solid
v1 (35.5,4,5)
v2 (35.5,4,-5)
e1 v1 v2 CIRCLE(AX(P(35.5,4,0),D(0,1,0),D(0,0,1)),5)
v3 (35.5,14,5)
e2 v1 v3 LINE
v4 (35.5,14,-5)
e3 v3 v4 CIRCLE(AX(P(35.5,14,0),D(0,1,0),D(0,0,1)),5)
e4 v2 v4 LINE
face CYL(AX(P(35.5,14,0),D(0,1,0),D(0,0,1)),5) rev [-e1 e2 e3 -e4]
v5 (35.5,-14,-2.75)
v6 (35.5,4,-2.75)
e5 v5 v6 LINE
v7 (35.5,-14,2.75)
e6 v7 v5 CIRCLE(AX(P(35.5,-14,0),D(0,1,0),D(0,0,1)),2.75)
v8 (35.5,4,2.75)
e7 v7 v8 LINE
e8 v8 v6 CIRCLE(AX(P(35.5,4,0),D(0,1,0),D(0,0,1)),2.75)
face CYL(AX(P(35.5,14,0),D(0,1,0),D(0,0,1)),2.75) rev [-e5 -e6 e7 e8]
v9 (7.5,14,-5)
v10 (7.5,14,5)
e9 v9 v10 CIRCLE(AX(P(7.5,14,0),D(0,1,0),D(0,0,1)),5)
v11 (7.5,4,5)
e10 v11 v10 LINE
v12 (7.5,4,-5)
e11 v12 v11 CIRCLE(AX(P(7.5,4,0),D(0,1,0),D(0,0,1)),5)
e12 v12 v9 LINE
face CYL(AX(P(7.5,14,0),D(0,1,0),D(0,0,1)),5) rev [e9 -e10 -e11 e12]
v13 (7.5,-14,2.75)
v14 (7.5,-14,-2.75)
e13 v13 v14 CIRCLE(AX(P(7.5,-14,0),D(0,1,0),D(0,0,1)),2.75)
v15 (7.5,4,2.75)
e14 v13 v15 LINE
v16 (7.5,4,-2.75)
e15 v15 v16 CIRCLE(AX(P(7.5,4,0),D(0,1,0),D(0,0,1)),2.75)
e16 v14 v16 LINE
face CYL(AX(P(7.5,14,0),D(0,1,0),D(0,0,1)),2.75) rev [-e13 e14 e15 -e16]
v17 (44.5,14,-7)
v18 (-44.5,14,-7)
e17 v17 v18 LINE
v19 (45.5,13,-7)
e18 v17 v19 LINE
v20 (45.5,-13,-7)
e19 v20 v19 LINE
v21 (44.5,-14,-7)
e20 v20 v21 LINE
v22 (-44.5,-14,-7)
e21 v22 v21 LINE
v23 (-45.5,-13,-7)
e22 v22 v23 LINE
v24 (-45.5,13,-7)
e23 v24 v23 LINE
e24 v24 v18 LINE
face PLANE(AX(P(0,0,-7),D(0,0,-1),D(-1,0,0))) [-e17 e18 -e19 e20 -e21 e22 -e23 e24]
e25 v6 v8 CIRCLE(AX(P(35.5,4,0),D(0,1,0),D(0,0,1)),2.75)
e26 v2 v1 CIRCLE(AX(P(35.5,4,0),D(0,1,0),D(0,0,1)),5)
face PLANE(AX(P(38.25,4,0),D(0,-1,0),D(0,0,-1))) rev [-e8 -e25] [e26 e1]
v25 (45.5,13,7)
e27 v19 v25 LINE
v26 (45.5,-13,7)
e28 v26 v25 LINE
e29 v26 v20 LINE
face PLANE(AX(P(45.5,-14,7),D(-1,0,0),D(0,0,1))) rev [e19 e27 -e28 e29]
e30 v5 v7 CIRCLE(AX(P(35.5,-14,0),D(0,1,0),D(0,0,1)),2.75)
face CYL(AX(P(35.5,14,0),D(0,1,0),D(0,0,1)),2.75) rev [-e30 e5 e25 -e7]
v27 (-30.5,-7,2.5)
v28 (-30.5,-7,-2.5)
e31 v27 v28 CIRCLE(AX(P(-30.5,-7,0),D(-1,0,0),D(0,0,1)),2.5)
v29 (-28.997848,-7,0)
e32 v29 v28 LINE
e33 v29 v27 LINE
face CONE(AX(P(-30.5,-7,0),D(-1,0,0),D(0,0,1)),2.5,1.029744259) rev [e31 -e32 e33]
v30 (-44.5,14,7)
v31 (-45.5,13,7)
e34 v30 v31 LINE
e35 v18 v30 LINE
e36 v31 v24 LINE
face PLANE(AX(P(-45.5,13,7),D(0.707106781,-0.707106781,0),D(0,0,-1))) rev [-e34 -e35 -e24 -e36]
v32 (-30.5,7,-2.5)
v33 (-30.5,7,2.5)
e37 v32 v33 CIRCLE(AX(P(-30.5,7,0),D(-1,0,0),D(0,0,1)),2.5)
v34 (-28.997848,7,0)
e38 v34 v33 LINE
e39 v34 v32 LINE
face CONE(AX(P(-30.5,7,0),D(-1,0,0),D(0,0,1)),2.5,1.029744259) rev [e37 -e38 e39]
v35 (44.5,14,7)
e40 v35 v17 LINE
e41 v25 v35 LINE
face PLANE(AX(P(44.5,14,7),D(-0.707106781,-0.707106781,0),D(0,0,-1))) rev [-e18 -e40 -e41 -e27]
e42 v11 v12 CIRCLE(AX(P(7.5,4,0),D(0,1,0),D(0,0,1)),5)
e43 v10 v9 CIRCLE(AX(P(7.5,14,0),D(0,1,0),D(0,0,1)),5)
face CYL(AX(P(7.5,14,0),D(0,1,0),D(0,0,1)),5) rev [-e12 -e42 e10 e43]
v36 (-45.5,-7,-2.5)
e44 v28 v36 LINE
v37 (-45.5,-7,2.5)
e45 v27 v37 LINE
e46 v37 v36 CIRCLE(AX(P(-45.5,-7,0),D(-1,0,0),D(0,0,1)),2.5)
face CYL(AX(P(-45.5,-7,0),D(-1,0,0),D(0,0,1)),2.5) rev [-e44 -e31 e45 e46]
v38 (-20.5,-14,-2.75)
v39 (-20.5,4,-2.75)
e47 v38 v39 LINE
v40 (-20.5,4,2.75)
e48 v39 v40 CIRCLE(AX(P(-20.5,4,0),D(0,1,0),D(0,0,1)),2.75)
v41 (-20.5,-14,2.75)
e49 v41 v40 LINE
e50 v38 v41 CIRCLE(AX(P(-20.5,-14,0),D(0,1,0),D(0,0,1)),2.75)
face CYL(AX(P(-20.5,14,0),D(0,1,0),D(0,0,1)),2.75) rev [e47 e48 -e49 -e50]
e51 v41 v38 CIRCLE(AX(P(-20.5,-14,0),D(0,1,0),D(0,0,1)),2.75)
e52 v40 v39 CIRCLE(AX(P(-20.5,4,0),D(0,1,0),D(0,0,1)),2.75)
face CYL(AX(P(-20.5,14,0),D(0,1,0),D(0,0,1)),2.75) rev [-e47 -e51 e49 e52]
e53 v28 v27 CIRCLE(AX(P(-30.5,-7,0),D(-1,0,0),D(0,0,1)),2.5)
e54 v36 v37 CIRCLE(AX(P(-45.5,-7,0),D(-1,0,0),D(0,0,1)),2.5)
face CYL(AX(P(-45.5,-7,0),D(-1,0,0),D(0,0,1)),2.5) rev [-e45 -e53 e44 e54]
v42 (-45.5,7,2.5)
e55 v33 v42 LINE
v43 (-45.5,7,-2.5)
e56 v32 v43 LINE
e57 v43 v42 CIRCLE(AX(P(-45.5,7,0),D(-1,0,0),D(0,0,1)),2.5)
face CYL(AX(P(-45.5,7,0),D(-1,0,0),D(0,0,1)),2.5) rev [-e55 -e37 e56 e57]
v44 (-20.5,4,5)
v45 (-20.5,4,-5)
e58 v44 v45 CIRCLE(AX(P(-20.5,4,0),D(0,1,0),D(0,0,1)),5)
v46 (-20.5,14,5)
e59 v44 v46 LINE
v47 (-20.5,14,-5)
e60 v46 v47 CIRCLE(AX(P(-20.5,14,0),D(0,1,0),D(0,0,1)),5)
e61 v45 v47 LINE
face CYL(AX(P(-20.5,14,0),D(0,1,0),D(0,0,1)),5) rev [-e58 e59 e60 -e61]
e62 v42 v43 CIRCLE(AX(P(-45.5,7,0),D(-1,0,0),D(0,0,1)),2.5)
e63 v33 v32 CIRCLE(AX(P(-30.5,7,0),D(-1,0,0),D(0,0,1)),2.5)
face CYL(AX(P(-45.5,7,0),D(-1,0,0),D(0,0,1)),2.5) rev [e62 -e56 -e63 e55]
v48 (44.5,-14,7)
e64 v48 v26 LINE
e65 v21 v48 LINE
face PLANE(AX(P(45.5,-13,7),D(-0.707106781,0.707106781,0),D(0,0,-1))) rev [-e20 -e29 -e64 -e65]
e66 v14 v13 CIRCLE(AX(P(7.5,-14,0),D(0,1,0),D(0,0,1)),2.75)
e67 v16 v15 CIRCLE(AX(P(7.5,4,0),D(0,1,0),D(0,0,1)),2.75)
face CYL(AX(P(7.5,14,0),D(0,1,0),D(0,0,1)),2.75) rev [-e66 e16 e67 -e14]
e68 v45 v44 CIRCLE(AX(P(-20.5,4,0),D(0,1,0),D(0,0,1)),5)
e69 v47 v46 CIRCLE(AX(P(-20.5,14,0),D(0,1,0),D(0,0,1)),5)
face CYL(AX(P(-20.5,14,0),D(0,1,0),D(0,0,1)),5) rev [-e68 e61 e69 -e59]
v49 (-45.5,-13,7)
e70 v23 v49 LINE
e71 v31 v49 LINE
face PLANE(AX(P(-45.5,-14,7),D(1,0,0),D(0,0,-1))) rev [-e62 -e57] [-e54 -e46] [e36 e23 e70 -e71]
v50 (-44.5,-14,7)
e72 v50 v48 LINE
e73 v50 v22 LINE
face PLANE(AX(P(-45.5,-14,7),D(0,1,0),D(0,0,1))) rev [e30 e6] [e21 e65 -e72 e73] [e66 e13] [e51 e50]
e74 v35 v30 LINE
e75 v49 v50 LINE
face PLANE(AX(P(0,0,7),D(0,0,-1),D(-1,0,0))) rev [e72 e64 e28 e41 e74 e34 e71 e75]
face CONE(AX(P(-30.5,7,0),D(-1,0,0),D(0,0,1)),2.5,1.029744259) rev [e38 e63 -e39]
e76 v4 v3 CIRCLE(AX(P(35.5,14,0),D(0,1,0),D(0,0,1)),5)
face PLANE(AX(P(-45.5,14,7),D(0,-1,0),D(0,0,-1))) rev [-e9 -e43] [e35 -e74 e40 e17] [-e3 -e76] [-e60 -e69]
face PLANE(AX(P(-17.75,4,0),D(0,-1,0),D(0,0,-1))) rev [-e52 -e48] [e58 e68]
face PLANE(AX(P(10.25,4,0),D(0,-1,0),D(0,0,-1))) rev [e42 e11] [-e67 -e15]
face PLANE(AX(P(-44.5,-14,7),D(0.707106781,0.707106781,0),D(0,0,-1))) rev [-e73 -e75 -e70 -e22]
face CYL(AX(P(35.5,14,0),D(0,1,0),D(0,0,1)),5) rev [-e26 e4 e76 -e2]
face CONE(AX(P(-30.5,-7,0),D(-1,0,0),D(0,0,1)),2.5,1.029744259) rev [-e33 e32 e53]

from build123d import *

# Parameters (mm, degrees)
SKETCH1_W                                            = 91
SKETCH1_H                                            = 28
BOSS_EXTRUDE1_DEPTH                                  = 7
M6_TAPPED_HOLE1_D                                    = 5
M6_TAPPED_HOLE1_DEPTH                                = 15
M6_TAPPED_HOLE1_TIP                                  = 1.502151548
HOLE_SIZE_PER_SOCKET_HEAD_CAP_SCREW_TYPE_D           = 5.5
HOLE_SIZE_PER_SOCKET_HEAD_CAP_SCREW_TYPE_CBORE_D     = 10
HOLE_SIZE_PER_SOCKET_HEAD_CAP_SCREW_TYPE_CBORE_DEPTH = 10
CHAMFER1_SIZE                                        = 1


with BuildPart() as part:
    # Sketch1 → Boss-Extrude1 (new, symmetric)
    with BuildSketch(Plane.XY):
        Rectangle(SKETCH1_W, SKETCH1_H)
    extrude(amount=BOSS_EXTRUDE1_DEPTH, both=True)

    # M6 Tapped Hole1
    with Locations(Plane.ZY.offset(45.5)):
        with Locations((0, -7), (0, 7)):
            Hole(M6_TAPPED_HOLE1_D / 2, depth=M6_TAPPED_HOLE1_DEPTH)
            with Locations((0, 0, -(M6_TAPPED_HOLE1_DEPTH + M6_TAPPED_HOLE1_TIP / 2))):  # 118° drill point
                Cone(0, M6_TAPPED_HOLE1_D / 2, M6_TAPPED_HOLE1_TIP, mode=Mode.SUBTRACT)

    # Hole Size per Socket Head Cap Screw Type1 (through all)
    with Locations(Plane(origin=(0, 14, 0), x_dir=(1, 0, 0), z_dir=(0, 1, 0))):
        with Locations((7.5, 0), (-20.5, 0), (35.5, 0)):
            CounterBoreHole(HOLE_SIZE_PER_SOCKET_HEAD_CAP_SCREW_TYPE_D / 2, HOLE_SIZE_PER_SOCKET_HEAD_CAP_SCREW_TYPE_CBORE_D / 2, HOLE_SIZE_PER_SOCKET_HEAD_CAP_SCREW_TYPE_CBORE_DEPTH)

    # Chamfer1
    chamfer1_edges = [part.edges().sort_by_distance(p)[0] for p in [
        (45.5, -14, 0),
        (-45.5, -14, 0),
        (-45.5, 14, 0),
        (45.5, 14, 0),
    ]]
    chamfer(chamfer1_edges, length=CHAMFER1_SIZE)


solid = part.part
